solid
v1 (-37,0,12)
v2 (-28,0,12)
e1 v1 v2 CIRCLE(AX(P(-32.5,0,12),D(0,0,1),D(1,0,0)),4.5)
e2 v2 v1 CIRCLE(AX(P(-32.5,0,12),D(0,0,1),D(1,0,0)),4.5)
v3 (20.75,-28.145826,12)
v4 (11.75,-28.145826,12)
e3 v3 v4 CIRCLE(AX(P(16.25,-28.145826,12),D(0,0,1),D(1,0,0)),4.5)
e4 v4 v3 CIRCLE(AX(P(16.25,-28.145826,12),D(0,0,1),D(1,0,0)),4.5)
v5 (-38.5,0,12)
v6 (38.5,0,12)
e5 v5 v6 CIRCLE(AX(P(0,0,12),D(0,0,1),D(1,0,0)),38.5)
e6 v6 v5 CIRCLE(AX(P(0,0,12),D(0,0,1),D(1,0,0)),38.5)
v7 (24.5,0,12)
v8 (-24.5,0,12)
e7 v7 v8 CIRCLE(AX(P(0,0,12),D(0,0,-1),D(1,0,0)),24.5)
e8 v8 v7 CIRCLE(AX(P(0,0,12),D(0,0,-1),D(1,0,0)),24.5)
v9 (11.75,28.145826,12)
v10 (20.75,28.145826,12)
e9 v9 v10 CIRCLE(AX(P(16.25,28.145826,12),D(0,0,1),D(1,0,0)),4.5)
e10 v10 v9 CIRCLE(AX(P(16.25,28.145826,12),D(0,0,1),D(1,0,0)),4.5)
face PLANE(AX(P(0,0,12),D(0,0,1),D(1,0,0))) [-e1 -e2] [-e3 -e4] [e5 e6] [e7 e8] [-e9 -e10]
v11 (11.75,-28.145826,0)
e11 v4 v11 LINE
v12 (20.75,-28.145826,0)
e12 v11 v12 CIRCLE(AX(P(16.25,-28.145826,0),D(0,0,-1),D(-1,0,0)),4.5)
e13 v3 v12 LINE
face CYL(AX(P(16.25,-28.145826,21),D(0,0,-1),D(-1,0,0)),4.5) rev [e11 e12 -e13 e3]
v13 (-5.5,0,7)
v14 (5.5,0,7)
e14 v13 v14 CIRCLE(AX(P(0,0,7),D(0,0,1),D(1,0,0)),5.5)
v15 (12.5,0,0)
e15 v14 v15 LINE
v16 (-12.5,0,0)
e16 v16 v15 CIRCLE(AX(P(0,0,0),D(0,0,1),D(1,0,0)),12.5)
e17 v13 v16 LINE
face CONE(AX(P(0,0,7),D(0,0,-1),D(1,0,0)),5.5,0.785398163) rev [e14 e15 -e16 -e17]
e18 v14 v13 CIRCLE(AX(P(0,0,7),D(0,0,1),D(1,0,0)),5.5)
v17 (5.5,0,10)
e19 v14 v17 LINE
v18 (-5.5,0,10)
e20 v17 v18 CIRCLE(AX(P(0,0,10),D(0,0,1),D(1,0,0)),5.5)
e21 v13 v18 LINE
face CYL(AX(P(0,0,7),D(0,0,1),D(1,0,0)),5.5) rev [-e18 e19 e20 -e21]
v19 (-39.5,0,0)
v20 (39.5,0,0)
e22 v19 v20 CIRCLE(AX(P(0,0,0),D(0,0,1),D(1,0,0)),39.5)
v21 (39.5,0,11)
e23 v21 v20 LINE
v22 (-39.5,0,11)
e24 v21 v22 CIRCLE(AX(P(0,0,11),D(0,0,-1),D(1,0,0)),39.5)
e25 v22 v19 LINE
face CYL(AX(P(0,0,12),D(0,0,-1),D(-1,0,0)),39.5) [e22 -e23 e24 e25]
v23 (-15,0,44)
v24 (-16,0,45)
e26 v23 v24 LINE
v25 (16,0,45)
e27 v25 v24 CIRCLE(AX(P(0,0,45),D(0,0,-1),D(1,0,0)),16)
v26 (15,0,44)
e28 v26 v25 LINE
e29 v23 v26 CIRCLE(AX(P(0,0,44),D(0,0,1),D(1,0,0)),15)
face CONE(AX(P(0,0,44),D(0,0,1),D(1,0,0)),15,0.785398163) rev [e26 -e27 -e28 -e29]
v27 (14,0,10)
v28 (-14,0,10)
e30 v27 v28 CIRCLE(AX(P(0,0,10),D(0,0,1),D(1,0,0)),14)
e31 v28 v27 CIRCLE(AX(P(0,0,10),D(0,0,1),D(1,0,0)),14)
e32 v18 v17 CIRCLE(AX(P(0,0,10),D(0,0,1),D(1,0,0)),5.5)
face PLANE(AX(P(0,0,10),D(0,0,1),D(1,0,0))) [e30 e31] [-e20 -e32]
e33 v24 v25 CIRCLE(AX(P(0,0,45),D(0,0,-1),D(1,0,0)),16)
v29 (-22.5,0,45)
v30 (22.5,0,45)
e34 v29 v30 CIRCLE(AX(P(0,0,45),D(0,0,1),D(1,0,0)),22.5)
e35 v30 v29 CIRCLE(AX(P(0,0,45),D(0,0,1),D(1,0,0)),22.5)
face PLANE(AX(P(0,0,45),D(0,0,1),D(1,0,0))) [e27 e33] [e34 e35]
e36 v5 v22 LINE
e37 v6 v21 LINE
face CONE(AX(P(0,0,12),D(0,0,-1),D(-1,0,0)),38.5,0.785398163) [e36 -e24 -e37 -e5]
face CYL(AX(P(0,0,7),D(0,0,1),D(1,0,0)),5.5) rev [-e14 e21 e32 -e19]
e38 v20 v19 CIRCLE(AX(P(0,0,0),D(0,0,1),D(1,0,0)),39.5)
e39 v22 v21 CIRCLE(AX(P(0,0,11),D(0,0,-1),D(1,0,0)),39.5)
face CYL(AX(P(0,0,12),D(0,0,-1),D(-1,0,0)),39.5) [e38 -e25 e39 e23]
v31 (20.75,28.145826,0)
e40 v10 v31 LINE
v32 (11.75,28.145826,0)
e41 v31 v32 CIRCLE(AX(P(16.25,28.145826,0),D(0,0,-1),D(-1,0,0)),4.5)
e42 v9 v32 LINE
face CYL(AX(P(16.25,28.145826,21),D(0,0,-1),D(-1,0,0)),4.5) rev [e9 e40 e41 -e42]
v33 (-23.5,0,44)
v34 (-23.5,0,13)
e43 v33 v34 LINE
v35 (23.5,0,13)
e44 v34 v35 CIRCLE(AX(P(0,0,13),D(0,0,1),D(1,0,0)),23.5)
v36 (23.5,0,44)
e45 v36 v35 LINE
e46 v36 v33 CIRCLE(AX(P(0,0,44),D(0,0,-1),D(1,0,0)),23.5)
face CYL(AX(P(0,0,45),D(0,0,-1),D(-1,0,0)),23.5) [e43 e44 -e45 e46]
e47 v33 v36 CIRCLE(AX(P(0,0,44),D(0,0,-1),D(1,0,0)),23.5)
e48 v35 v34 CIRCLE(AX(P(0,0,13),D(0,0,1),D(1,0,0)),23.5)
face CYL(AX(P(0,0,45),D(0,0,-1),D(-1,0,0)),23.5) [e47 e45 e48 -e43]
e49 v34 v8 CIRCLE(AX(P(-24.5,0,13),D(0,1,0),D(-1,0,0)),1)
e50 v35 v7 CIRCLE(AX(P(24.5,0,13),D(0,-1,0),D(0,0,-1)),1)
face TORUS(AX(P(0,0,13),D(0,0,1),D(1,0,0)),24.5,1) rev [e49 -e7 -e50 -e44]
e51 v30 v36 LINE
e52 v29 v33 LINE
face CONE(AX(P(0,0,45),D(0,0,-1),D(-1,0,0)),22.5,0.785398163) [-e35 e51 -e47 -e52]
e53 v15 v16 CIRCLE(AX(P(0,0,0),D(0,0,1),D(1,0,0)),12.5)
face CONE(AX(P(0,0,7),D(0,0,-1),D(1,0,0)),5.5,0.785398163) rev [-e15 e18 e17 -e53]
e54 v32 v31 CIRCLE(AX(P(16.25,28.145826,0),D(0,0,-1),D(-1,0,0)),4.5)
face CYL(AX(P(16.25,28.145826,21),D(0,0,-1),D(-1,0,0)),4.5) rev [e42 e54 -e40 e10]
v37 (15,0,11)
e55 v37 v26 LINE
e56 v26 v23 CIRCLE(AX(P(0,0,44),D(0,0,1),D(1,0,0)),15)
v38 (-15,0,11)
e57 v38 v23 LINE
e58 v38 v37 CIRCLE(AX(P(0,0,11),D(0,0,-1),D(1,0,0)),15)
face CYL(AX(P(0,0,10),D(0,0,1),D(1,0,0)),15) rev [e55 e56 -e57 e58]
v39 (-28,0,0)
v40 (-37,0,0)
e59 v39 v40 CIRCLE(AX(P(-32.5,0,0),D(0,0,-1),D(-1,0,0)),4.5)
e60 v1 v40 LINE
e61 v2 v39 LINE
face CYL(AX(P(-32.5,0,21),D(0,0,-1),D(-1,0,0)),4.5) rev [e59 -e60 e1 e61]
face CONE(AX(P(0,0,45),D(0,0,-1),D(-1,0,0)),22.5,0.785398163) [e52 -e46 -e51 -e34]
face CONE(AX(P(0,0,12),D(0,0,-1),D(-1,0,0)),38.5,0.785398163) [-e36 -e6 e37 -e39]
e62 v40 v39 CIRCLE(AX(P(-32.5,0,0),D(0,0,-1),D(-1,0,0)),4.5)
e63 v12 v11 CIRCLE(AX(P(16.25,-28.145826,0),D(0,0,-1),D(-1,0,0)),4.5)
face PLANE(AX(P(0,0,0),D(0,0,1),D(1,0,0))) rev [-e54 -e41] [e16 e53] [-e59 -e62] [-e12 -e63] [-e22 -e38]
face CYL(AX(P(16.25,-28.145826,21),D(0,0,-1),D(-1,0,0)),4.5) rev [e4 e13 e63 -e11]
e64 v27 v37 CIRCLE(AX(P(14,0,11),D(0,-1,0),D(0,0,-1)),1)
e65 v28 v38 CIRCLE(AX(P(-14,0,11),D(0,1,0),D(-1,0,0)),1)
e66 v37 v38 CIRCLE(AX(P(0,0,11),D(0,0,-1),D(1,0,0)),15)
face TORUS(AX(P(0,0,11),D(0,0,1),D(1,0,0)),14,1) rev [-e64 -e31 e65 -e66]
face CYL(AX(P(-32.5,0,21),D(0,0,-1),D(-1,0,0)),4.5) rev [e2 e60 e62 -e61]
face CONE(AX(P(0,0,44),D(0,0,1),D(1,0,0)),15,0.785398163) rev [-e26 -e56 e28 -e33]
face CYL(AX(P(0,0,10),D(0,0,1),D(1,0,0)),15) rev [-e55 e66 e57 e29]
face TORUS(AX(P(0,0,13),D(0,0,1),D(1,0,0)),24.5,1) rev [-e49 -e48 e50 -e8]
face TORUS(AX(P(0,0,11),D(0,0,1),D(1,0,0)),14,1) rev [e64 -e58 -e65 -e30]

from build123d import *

# Parameters (mm, degrees)
SKETCH1_R           = 39.5
BOSS_EXTRUDE1_DEPTH = 12
SKETCH2_R           = 23.5
BOSS_EXTRUDE2_DEPTH = 33
SKETCH3_R           = 15
CUT_EXTRUDE1_DEPTH  = 35
SKETCH4_R           = 5.5
CUT_EXTRUDE2_DEPTH  = 3
SKETCH5_R           = 5.5
CUT_EXTRUDE3_DEPTH  = 7
CUT_EXTRUDE3_DRAFT  = 45
CHAMFER1_SIZE       = 1
SKETCH6_R           = 4.5
CUT_EXTRUDE4_DEPTH  = 21
FILLET1_R           = 1


with BuildPart() as part:
    # Sketch1 → Boss-Extrude1 (new body)
    with BuildSketch(Plane.XY):
        Circle(SKETCH1_R)
    extrude(amount=BOSS_EXTRUDE1_DEPTH)

    # Sketch2 → Boss-Extrude2 (add)
    with BuildSketch(Plane.XY.offset(12)):
        Circle(SKETCH2_R)
    extrude(amount=BOSS_EXTRUDE2_DEPTH)

    # Sketch3 → Cut-Extrude1 (cut)
    with BuildSketch(Plane.XY.offset(45)):
        Circle(SKETCH3_R)
    extrude(amount=-CUT_EXTRUDE1_DEPTH, mode=Mode.SUBTRACT)

    # Sketch4 → Cut-Extrude2 (cut)
    with BuildSketch(Plane.XY.offset(10)):
        Circle(SKETCH4_R)
    extrude(amount=-CUT_EXTRUDE2_DEPTH, mode=Mode.SUBTRACT)


with BuildPart() as cut_extrude3_tool:
    # Sketch5 → Cut-Extrude3 (with draft: the straight prism first)
    with BuildSketch(Plane.XY.offset(7)):
        Circle(SKETCH5_R)
    extrude(amount=-CUT_EXTRUDE3_DEPTH)
    # Cut-Extrude3: the draft: its side faces are tilted about the plane it starts from
    cut_extrude3_sides = [cut_extrude3_tool.faces().sort_by_distance(p)[0] for p in [
        (-5.5, 0, 3.5),
    ]]
    draft(cut_extrude3_sides, Plane.XY.offset(7), CUT_EXTRUDE3_DRAFT)


with BuildPart() as part_1:
    add(part.part)

    # Cut-Extrude3: cut by cut_extrude3_tool
    add(cut_extrude3_tool.part, mode=Mode.SUBTRACT)

    # Chamfer1
    chamfer1_edges = [part_1.edges().sort_by_distance(p)[0] for p in [
        (-15, 0, 45),
        (-39.5, 0, 12),
        (-23.5, 0, 45),
    ]]
    chamfer(chamfer1_edges, length=CHAMFER1_SIZE)

    # Sketch6 → Cut-Extrude4 (cut)
    with BuildSketch(Plane(origin=(0, 0, 0), x_dir=(-1, 0, 0), z_dir=(0, 0, -1))):
        with Locations((32.5, 0)):
            Circle(SKETCH6_R)
        with Locations((-16.25, -28.145825623)):
            Circle(SKETCH6_R)
        with Locations((-16.25, 28.145825623)):
            Circle(SKETCH6_R)
    extrude(amount=-CUT_EXTRUDE4_DEPTH, mode=Mode.SUBTRACT)

    # Fillet1
    fillet1_edges = [part_1.edges().sort_by_distance(p)[0] for p in [
        (-15, 0, 10),
        (-23.5, 0, 12),
    ]]
    fillet(fillet1_edges, radius=FILLET1_R)


solid = part_1.part
